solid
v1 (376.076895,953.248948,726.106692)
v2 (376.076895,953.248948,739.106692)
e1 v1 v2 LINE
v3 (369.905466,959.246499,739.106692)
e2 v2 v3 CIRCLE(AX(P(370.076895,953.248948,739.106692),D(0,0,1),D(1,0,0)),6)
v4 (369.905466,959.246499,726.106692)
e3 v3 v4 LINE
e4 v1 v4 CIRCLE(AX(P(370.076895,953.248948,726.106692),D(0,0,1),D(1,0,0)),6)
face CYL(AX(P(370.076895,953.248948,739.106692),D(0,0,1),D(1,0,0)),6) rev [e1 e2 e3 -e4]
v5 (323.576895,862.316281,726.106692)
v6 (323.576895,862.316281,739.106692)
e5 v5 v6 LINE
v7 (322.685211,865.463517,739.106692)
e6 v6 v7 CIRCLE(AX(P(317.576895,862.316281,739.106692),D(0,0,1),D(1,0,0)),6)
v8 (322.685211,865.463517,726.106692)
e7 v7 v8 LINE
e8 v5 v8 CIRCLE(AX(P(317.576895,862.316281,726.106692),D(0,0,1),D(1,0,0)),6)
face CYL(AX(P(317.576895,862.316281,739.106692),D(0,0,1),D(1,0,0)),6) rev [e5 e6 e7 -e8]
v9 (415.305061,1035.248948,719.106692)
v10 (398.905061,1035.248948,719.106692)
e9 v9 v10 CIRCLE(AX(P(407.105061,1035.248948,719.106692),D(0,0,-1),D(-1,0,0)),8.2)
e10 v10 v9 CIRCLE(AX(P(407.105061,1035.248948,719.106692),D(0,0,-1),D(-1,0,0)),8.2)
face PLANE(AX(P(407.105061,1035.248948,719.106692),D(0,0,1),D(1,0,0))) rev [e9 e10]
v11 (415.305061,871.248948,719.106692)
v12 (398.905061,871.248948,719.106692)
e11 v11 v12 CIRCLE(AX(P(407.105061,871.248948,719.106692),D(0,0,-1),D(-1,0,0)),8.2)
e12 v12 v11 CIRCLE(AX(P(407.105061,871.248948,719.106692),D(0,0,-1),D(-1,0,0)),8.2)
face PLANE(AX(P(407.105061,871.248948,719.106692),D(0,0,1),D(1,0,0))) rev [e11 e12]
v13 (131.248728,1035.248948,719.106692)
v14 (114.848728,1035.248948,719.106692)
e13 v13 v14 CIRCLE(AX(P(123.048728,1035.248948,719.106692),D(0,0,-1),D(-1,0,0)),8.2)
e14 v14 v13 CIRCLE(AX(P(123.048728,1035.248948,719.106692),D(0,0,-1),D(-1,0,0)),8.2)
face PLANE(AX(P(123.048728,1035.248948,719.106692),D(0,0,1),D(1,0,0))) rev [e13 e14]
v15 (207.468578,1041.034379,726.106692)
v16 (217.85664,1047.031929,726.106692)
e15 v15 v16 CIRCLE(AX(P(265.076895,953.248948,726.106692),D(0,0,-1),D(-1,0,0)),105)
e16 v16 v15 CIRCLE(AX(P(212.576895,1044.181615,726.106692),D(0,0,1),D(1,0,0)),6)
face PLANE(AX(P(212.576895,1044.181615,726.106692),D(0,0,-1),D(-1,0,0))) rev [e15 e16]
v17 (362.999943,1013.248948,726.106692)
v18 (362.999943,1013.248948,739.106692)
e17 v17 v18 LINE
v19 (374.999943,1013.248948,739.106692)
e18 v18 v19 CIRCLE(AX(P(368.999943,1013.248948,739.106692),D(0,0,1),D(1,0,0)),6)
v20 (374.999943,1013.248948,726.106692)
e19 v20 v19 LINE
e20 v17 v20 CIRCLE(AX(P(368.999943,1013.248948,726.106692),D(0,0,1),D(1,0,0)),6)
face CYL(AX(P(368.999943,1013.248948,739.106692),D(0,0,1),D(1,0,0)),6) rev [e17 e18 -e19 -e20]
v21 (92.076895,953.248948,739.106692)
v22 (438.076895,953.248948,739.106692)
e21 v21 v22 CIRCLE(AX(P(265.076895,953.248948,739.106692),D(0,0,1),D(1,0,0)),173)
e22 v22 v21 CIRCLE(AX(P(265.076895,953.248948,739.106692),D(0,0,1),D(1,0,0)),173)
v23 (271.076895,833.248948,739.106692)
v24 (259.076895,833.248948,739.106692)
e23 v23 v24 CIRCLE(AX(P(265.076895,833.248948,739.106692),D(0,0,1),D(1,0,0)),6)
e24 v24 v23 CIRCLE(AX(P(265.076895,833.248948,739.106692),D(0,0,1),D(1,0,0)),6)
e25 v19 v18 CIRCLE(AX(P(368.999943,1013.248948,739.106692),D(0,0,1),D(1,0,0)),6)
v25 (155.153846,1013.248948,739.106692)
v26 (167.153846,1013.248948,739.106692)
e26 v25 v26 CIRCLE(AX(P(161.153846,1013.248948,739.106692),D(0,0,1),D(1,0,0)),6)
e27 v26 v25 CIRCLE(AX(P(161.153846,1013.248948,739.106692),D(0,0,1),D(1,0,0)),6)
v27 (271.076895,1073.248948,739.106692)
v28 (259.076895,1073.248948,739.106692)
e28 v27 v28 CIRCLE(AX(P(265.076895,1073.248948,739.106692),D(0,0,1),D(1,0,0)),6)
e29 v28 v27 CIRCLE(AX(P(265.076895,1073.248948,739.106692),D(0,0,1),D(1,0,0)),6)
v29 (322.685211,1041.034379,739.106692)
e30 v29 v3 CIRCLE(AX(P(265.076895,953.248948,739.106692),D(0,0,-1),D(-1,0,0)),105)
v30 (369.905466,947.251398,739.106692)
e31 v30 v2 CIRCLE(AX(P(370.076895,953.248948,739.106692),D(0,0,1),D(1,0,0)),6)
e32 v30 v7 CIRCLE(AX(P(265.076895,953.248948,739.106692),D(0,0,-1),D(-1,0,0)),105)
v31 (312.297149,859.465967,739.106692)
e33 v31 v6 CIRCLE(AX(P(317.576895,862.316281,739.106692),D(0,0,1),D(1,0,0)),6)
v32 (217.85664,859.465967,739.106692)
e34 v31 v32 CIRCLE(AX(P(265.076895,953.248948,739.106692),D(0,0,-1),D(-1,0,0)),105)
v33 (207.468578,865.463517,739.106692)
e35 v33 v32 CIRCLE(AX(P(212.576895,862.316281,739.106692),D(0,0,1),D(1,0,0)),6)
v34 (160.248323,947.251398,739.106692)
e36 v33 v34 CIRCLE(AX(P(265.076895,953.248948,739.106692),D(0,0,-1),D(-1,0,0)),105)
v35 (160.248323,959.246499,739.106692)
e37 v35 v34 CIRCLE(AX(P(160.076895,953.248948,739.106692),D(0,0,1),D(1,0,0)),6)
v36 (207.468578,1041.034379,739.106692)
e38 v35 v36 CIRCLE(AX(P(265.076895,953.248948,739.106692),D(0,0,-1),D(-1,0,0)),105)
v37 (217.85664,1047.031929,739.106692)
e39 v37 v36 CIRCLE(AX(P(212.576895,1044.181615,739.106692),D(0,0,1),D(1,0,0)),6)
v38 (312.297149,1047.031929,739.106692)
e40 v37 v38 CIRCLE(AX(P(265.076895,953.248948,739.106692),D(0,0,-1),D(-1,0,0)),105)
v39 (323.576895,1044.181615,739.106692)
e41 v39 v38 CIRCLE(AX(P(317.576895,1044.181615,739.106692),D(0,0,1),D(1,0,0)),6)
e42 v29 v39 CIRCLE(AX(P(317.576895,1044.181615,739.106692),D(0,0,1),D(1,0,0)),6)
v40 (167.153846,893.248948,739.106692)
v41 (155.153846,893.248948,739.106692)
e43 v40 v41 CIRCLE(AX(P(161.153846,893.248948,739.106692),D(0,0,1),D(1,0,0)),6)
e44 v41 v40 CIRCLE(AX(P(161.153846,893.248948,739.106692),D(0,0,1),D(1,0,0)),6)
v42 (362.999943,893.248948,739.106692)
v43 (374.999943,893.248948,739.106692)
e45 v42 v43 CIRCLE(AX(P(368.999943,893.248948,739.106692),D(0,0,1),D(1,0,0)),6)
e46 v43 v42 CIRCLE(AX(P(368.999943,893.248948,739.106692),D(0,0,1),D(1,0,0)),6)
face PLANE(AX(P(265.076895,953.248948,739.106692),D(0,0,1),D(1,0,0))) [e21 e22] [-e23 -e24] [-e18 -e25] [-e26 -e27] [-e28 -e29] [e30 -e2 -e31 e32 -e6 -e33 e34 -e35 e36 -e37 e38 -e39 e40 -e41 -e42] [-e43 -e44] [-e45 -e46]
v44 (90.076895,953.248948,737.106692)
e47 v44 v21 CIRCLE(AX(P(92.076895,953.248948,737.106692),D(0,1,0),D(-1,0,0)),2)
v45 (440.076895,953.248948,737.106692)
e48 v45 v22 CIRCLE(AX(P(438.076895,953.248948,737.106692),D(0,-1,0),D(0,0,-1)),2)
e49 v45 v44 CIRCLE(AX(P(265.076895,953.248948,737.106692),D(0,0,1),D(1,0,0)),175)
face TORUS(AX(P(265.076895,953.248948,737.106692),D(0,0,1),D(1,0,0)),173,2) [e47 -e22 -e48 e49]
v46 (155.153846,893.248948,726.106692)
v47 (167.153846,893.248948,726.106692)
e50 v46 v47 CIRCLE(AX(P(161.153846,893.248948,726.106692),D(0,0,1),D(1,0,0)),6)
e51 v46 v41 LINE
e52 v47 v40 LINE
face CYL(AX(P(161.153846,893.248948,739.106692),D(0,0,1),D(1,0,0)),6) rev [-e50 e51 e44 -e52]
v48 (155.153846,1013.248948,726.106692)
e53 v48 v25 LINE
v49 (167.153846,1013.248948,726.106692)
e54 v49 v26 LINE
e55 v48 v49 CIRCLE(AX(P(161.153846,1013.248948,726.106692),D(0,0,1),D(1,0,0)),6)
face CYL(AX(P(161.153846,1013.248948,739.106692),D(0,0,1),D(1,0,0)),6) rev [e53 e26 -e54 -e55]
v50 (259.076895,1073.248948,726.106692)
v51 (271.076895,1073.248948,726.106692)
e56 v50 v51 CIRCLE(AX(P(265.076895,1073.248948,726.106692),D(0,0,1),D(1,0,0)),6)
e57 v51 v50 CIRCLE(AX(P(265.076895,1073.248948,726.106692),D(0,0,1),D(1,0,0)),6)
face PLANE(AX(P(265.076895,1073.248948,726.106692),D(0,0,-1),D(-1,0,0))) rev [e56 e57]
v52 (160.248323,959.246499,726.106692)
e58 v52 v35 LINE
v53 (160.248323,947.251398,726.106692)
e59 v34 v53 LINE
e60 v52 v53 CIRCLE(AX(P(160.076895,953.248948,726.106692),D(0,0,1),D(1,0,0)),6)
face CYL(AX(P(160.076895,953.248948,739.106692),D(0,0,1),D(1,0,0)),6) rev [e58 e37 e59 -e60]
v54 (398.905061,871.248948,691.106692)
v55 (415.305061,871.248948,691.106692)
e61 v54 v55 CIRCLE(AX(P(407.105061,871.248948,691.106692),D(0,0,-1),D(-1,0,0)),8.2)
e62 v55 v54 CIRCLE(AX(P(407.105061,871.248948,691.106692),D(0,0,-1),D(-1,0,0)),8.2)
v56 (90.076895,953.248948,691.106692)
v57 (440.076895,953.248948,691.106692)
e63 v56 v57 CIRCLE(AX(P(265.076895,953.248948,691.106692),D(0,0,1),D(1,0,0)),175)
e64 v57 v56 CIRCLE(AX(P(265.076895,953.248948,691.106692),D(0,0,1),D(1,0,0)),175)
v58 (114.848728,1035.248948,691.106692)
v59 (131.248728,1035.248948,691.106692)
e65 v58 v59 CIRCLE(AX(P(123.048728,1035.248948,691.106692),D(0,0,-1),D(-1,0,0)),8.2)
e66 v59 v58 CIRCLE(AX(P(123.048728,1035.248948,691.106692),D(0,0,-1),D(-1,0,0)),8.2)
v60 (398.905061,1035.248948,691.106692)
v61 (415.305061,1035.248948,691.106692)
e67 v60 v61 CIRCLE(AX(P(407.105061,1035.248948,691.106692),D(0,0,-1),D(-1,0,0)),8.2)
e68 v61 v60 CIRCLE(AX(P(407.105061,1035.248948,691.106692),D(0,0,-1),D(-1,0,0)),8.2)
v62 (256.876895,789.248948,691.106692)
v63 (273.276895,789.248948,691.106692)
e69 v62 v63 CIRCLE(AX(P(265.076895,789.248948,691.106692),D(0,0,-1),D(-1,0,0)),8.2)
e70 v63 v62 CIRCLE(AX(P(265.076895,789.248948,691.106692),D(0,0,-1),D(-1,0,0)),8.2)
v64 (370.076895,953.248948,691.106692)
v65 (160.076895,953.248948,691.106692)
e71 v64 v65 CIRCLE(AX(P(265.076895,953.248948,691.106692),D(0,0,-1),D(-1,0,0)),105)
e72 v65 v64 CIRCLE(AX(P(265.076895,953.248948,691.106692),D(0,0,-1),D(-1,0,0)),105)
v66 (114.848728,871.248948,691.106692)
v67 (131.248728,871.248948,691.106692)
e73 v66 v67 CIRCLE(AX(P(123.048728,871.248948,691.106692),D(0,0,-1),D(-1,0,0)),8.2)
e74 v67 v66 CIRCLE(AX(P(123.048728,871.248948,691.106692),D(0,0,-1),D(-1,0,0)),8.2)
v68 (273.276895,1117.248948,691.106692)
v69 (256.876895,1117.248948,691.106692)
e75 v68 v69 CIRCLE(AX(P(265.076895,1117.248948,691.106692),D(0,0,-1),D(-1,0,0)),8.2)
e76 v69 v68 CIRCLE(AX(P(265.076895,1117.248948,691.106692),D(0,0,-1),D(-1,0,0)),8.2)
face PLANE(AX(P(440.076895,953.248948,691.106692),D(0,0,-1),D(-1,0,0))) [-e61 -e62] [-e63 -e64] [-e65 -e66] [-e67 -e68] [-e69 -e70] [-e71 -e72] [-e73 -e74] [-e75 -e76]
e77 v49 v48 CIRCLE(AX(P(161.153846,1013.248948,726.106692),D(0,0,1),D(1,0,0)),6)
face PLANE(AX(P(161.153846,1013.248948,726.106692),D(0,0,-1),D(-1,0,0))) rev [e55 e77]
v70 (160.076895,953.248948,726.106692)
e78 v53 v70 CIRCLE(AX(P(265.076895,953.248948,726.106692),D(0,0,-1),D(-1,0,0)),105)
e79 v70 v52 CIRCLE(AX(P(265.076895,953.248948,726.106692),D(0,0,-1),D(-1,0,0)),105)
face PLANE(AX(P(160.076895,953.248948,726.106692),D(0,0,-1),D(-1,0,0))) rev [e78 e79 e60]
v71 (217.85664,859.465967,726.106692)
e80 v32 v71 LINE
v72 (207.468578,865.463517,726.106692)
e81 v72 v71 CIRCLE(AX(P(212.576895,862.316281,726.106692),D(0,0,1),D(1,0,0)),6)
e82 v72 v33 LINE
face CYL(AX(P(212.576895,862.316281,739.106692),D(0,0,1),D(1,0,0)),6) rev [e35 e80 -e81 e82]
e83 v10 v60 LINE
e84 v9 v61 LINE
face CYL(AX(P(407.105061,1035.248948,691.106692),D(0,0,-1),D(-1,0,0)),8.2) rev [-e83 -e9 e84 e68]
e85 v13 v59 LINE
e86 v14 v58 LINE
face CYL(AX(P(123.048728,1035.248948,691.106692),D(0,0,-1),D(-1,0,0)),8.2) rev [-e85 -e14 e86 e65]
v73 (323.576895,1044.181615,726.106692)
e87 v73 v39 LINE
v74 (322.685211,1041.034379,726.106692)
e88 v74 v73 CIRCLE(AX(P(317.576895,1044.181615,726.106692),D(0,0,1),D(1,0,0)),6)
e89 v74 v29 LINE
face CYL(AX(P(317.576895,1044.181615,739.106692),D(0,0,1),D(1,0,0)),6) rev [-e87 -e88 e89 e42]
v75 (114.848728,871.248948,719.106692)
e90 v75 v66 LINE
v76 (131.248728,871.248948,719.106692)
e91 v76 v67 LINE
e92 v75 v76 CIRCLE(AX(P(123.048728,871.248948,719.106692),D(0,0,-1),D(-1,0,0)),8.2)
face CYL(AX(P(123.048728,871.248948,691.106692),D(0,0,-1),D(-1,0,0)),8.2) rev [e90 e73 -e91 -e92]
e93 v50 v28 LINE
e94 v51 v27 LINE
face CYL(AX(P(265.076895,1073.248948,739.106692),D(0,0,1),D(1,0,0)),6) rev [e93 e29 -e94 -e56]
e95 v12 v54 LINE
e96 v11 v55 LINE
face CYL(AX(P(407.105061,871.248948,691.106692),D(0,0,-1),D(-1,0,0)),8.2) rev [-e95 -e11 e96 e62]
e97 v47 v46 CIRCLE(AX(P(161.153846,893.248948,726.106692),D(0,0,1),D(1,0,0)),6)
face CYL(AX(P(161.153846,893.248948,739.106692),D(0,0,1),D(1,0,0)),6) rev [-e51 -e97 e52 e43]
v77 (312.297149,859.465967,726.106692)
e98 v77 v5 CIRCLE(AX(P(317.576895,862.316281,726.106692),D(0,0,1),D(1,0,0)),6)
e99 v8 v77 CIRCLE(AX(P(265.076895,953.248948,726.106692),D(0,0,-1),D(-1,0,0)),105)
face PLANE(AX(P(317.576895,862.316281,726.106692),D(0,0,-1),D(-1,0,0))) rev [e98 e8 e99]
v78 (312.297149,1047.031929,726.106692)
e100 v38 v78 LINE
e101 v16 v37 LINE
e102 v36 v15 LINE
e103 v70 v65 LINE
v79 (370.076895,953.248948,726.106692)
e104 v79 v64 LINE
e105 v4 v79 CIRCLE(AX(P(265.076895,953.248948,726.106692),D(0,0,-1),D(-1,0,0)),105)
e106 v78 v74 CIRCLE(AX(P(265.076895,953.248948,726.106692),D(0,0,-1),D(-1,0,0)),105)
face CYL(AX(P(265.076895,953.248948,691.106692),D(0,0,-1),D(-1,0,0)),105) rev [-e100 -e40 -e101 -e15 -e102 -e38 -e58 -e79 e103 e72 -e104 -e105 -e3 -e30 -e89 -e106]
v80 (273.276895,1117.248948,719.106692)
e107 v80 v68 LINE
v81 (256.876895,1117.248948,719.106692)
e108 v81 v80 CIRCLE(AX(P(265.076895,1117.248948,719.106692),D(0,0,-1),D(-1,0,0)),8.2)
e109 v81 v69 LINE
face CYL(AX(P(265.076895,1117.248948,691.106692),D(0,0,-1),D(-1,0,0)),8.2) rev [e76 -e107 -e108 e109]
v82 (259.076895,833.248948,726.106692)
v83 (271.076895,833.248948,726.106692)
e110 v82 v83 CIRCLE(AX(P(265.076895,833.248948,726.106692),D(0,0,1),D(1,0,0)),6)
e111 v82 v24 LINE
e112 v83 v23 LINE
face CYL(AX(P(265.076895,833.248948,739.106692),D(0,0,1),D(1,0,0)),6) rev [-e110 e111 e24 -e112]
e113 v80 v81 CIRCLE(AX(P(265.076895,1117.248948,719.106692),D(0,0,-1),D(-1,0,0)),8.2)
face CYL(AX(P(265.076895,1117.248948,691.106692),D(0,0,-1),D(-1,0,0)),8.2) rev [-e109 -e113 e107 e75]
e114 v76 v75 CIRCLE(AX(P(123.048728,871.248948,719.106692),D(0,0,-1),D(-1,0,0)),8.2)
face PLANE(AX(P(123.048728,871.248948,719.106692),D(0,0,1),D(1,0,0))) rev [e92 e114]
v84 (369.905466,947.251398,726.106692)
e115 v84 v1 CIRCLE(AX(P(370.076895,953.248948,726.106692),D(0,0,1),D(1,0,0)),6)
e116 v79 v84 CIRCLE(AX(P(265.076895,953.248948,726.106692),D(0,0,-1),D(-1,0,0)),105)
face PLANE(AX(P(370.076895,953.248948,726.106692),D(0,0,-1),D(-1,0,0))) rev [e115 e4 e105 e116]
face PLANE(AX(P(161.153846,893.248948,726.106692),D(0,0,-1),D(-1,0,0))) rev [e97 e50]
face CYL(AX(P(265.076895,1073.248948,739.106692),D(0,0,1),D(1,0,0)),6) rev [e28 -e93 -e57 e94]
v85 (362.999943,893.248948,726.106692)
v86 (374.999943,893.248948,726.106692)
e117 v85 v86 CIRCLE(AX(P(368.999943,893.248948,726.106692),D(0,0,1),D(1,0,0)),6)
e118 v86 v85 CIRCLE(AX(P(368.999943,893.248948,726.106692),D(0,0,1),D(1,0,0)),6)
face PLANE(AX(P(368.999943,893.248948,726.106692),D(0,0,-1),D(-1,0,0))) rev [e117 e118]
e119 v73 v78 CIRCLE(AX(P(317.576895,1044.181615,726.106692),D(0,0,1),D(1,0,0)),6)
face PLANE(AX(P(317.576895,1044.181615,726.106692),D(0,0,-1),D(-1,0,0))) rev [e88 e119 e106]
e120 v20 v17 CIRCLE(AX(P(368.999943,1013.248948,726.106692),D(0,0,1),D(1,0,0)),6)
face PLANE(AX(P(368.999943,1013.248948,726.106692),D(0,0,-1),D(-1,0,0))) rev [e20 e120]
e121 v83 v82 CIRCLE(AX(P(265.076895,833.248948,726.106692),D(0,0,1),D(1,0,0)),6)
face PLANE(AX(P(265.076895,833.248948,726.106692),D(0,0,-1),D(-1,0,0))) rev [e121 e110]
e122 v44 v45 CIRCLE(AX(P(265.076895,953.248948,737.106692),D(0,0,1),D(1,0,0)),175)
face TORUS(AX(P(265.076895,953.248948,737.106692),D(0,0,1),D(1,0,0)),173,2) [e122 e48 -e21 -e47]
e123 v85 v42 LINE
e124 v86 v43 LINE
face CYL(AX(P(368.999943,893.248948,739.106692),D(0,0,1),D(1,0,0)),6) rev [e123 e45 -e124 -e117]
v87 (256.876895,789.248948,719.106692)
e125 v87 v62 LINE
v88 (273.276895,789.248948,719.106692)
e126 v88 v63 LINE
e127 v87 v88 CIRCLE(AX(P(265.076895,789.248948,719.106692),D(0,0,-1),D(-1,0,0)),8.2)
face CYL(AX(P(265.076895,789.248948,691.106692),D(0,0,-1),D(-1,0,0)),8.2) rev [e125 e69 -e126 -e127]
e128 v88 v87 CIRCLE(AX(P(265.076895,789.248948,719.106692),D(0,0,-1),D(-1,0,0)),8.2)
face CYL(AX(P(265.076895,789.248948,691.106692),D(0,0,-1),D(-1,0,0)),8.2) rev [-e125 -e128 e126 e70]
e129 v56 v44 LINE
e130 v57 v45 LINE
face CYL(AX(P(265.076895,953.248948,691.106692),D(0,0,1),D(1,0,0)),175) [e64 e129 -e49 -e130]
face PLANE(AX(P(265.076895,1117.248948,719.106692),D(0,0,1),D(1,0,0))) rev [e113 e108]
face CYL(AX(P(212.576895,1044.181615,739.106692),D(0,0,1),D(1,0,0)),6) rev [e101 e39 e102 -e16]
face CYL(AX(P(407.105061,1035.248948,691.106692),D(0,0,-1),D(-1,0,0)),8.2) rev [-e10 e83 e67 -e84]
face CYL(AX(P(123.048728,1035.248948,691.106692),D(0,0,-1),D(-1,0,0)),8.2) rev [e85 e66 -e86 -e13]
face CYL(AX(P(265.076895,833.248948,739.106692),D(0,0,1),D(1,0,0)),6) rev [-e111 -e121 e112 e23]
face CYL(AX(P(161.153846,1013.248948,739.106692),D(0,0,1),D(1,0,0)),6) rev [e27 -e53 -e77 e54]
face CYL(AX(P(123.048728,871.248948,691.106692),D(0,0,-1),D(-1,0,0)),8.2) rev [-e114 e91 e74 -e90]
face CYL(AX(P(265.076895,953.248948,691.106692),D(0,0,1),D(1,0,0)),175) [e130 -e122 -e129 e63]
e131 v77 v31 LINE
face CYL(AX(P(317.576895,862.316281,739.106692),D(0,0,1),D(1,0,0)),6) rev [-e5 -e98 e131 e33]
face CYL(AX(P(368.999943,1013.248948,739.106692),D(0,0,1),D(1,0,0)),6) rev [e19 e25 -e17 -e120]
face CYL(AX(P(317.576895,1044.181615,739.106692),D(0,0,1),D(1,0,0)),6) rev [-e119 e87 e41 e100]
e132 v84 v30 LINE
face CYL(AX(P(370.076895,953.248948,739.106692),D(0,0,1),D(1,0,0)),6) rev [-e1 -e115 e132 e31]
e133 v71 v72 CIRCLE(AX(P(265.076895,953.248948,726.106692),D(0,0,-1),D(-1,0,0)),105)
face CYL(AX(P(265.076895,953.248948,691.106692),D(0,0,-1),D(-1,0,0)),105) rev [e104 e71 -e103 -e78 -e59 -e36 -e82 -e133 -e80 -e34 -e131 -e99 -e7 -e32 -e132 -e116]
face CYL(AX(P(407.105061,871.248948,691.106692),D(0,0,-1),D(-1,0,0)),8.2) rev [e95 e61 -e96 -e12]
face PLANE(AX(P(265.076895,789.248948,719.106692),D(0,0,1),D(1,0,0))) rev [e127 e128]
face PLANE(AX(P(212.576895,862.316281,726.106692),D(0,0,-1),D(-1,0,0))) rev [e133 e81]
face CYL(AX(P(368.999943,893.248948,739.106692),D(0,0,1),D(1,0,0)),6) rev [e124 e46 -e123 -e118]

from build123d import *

# Parameters (mm, degrees)
M14_CLEARANCE_HOLE1_D          = 16.4
M14_CLEARANCE_HOLE1_DEPTH      = 28
F_12_0_12_DIAMETER_HOLE1_D     = 12
F_12_0_12_DIAMETER_HOLE1_DEPTH = 13
HOLE1_D                        = 210


with BuildPart() as part:
    # Sketch1 → Revolve1 (revolve)
    with BuildSketch(Plane(origin=(0, 953.248948069, 0), x_dir=(1, 0, 0), z_dir=(0, 1, 0))):
        with BuildLine():
            Line((440.076894512, -691.106692253), (265.076894512, -691.106692253))
            Line((265.076894512, -691.106692253), (265.076894512, -739.106692253))
            Line((265.076894512, -739.106692253), (438.076894512, -739.106692253))
            ThreePointArc((438.076894512, -739.106692253), (439.491108075, -738.520905816), (440.076894512, -737.106692253))
            Line((440.076894512, -737.106692253), (440.076894512, -691.106692253))
        make_face()
    revolve(axis=Axis((265.076894512, 953.248948069, 691.106692253), (0, 0, 1)))

    # M14 Clearance Hole1
    with Locations(Plane(origin=(0, 0, 691.106692253), x_dir=(-1, 0, 0), z_dir=(0, 0, -1))):
        with Locations((-123.048728292, 1035.248948069), (-123.048728292, 871.248948069), (-265.076894512, 789.248948069), (-407.105060733, 871.248948069), (-407.105060733, 1035.248948069), (-265.076894512, 1117.248948069)):
            Hole(M14_CLEARANCE_HOLE1_D / 2, depth=M14_CLEARANCE_HOLE1_DEPTH)

    # Ø12.0 (12) Diameter Hole1
    with Locations(Plane.XY.offset(739.106692253)):
        with Locations((370.076894512, 953.248948069), (317.576894512, 1044.181615466), (160.076894512, 953.248948069), (212.576894512, 862.316280672), (317.576894512, 862.316280672), (212.576894512, 1044.181615466), (265.076894512, 833.248948069), (161.153846058, 893.248948069), (161.153846058, 1013.248948069), (265.076894512, 1073.248948069), (368.999942966, 1013.248948069), (368.999942966, 893.248948069)):
            Hole(F_12_0_12_DIAMETER_HOLE1_D / 2, depth=F_12_0_12_DIAMETER_HOLE1_DEPTH)

    # Hole1 (through all)
    with Locations(Plane(origin=(0, 0, 691.106692253), x_dir=(-1, 0, 0), z_dir=(0, 0, -1))):
        with Locations((-265.076894512, 953.248948069)):
            Hole(HOLE1_D / 2)


solid = part.part
